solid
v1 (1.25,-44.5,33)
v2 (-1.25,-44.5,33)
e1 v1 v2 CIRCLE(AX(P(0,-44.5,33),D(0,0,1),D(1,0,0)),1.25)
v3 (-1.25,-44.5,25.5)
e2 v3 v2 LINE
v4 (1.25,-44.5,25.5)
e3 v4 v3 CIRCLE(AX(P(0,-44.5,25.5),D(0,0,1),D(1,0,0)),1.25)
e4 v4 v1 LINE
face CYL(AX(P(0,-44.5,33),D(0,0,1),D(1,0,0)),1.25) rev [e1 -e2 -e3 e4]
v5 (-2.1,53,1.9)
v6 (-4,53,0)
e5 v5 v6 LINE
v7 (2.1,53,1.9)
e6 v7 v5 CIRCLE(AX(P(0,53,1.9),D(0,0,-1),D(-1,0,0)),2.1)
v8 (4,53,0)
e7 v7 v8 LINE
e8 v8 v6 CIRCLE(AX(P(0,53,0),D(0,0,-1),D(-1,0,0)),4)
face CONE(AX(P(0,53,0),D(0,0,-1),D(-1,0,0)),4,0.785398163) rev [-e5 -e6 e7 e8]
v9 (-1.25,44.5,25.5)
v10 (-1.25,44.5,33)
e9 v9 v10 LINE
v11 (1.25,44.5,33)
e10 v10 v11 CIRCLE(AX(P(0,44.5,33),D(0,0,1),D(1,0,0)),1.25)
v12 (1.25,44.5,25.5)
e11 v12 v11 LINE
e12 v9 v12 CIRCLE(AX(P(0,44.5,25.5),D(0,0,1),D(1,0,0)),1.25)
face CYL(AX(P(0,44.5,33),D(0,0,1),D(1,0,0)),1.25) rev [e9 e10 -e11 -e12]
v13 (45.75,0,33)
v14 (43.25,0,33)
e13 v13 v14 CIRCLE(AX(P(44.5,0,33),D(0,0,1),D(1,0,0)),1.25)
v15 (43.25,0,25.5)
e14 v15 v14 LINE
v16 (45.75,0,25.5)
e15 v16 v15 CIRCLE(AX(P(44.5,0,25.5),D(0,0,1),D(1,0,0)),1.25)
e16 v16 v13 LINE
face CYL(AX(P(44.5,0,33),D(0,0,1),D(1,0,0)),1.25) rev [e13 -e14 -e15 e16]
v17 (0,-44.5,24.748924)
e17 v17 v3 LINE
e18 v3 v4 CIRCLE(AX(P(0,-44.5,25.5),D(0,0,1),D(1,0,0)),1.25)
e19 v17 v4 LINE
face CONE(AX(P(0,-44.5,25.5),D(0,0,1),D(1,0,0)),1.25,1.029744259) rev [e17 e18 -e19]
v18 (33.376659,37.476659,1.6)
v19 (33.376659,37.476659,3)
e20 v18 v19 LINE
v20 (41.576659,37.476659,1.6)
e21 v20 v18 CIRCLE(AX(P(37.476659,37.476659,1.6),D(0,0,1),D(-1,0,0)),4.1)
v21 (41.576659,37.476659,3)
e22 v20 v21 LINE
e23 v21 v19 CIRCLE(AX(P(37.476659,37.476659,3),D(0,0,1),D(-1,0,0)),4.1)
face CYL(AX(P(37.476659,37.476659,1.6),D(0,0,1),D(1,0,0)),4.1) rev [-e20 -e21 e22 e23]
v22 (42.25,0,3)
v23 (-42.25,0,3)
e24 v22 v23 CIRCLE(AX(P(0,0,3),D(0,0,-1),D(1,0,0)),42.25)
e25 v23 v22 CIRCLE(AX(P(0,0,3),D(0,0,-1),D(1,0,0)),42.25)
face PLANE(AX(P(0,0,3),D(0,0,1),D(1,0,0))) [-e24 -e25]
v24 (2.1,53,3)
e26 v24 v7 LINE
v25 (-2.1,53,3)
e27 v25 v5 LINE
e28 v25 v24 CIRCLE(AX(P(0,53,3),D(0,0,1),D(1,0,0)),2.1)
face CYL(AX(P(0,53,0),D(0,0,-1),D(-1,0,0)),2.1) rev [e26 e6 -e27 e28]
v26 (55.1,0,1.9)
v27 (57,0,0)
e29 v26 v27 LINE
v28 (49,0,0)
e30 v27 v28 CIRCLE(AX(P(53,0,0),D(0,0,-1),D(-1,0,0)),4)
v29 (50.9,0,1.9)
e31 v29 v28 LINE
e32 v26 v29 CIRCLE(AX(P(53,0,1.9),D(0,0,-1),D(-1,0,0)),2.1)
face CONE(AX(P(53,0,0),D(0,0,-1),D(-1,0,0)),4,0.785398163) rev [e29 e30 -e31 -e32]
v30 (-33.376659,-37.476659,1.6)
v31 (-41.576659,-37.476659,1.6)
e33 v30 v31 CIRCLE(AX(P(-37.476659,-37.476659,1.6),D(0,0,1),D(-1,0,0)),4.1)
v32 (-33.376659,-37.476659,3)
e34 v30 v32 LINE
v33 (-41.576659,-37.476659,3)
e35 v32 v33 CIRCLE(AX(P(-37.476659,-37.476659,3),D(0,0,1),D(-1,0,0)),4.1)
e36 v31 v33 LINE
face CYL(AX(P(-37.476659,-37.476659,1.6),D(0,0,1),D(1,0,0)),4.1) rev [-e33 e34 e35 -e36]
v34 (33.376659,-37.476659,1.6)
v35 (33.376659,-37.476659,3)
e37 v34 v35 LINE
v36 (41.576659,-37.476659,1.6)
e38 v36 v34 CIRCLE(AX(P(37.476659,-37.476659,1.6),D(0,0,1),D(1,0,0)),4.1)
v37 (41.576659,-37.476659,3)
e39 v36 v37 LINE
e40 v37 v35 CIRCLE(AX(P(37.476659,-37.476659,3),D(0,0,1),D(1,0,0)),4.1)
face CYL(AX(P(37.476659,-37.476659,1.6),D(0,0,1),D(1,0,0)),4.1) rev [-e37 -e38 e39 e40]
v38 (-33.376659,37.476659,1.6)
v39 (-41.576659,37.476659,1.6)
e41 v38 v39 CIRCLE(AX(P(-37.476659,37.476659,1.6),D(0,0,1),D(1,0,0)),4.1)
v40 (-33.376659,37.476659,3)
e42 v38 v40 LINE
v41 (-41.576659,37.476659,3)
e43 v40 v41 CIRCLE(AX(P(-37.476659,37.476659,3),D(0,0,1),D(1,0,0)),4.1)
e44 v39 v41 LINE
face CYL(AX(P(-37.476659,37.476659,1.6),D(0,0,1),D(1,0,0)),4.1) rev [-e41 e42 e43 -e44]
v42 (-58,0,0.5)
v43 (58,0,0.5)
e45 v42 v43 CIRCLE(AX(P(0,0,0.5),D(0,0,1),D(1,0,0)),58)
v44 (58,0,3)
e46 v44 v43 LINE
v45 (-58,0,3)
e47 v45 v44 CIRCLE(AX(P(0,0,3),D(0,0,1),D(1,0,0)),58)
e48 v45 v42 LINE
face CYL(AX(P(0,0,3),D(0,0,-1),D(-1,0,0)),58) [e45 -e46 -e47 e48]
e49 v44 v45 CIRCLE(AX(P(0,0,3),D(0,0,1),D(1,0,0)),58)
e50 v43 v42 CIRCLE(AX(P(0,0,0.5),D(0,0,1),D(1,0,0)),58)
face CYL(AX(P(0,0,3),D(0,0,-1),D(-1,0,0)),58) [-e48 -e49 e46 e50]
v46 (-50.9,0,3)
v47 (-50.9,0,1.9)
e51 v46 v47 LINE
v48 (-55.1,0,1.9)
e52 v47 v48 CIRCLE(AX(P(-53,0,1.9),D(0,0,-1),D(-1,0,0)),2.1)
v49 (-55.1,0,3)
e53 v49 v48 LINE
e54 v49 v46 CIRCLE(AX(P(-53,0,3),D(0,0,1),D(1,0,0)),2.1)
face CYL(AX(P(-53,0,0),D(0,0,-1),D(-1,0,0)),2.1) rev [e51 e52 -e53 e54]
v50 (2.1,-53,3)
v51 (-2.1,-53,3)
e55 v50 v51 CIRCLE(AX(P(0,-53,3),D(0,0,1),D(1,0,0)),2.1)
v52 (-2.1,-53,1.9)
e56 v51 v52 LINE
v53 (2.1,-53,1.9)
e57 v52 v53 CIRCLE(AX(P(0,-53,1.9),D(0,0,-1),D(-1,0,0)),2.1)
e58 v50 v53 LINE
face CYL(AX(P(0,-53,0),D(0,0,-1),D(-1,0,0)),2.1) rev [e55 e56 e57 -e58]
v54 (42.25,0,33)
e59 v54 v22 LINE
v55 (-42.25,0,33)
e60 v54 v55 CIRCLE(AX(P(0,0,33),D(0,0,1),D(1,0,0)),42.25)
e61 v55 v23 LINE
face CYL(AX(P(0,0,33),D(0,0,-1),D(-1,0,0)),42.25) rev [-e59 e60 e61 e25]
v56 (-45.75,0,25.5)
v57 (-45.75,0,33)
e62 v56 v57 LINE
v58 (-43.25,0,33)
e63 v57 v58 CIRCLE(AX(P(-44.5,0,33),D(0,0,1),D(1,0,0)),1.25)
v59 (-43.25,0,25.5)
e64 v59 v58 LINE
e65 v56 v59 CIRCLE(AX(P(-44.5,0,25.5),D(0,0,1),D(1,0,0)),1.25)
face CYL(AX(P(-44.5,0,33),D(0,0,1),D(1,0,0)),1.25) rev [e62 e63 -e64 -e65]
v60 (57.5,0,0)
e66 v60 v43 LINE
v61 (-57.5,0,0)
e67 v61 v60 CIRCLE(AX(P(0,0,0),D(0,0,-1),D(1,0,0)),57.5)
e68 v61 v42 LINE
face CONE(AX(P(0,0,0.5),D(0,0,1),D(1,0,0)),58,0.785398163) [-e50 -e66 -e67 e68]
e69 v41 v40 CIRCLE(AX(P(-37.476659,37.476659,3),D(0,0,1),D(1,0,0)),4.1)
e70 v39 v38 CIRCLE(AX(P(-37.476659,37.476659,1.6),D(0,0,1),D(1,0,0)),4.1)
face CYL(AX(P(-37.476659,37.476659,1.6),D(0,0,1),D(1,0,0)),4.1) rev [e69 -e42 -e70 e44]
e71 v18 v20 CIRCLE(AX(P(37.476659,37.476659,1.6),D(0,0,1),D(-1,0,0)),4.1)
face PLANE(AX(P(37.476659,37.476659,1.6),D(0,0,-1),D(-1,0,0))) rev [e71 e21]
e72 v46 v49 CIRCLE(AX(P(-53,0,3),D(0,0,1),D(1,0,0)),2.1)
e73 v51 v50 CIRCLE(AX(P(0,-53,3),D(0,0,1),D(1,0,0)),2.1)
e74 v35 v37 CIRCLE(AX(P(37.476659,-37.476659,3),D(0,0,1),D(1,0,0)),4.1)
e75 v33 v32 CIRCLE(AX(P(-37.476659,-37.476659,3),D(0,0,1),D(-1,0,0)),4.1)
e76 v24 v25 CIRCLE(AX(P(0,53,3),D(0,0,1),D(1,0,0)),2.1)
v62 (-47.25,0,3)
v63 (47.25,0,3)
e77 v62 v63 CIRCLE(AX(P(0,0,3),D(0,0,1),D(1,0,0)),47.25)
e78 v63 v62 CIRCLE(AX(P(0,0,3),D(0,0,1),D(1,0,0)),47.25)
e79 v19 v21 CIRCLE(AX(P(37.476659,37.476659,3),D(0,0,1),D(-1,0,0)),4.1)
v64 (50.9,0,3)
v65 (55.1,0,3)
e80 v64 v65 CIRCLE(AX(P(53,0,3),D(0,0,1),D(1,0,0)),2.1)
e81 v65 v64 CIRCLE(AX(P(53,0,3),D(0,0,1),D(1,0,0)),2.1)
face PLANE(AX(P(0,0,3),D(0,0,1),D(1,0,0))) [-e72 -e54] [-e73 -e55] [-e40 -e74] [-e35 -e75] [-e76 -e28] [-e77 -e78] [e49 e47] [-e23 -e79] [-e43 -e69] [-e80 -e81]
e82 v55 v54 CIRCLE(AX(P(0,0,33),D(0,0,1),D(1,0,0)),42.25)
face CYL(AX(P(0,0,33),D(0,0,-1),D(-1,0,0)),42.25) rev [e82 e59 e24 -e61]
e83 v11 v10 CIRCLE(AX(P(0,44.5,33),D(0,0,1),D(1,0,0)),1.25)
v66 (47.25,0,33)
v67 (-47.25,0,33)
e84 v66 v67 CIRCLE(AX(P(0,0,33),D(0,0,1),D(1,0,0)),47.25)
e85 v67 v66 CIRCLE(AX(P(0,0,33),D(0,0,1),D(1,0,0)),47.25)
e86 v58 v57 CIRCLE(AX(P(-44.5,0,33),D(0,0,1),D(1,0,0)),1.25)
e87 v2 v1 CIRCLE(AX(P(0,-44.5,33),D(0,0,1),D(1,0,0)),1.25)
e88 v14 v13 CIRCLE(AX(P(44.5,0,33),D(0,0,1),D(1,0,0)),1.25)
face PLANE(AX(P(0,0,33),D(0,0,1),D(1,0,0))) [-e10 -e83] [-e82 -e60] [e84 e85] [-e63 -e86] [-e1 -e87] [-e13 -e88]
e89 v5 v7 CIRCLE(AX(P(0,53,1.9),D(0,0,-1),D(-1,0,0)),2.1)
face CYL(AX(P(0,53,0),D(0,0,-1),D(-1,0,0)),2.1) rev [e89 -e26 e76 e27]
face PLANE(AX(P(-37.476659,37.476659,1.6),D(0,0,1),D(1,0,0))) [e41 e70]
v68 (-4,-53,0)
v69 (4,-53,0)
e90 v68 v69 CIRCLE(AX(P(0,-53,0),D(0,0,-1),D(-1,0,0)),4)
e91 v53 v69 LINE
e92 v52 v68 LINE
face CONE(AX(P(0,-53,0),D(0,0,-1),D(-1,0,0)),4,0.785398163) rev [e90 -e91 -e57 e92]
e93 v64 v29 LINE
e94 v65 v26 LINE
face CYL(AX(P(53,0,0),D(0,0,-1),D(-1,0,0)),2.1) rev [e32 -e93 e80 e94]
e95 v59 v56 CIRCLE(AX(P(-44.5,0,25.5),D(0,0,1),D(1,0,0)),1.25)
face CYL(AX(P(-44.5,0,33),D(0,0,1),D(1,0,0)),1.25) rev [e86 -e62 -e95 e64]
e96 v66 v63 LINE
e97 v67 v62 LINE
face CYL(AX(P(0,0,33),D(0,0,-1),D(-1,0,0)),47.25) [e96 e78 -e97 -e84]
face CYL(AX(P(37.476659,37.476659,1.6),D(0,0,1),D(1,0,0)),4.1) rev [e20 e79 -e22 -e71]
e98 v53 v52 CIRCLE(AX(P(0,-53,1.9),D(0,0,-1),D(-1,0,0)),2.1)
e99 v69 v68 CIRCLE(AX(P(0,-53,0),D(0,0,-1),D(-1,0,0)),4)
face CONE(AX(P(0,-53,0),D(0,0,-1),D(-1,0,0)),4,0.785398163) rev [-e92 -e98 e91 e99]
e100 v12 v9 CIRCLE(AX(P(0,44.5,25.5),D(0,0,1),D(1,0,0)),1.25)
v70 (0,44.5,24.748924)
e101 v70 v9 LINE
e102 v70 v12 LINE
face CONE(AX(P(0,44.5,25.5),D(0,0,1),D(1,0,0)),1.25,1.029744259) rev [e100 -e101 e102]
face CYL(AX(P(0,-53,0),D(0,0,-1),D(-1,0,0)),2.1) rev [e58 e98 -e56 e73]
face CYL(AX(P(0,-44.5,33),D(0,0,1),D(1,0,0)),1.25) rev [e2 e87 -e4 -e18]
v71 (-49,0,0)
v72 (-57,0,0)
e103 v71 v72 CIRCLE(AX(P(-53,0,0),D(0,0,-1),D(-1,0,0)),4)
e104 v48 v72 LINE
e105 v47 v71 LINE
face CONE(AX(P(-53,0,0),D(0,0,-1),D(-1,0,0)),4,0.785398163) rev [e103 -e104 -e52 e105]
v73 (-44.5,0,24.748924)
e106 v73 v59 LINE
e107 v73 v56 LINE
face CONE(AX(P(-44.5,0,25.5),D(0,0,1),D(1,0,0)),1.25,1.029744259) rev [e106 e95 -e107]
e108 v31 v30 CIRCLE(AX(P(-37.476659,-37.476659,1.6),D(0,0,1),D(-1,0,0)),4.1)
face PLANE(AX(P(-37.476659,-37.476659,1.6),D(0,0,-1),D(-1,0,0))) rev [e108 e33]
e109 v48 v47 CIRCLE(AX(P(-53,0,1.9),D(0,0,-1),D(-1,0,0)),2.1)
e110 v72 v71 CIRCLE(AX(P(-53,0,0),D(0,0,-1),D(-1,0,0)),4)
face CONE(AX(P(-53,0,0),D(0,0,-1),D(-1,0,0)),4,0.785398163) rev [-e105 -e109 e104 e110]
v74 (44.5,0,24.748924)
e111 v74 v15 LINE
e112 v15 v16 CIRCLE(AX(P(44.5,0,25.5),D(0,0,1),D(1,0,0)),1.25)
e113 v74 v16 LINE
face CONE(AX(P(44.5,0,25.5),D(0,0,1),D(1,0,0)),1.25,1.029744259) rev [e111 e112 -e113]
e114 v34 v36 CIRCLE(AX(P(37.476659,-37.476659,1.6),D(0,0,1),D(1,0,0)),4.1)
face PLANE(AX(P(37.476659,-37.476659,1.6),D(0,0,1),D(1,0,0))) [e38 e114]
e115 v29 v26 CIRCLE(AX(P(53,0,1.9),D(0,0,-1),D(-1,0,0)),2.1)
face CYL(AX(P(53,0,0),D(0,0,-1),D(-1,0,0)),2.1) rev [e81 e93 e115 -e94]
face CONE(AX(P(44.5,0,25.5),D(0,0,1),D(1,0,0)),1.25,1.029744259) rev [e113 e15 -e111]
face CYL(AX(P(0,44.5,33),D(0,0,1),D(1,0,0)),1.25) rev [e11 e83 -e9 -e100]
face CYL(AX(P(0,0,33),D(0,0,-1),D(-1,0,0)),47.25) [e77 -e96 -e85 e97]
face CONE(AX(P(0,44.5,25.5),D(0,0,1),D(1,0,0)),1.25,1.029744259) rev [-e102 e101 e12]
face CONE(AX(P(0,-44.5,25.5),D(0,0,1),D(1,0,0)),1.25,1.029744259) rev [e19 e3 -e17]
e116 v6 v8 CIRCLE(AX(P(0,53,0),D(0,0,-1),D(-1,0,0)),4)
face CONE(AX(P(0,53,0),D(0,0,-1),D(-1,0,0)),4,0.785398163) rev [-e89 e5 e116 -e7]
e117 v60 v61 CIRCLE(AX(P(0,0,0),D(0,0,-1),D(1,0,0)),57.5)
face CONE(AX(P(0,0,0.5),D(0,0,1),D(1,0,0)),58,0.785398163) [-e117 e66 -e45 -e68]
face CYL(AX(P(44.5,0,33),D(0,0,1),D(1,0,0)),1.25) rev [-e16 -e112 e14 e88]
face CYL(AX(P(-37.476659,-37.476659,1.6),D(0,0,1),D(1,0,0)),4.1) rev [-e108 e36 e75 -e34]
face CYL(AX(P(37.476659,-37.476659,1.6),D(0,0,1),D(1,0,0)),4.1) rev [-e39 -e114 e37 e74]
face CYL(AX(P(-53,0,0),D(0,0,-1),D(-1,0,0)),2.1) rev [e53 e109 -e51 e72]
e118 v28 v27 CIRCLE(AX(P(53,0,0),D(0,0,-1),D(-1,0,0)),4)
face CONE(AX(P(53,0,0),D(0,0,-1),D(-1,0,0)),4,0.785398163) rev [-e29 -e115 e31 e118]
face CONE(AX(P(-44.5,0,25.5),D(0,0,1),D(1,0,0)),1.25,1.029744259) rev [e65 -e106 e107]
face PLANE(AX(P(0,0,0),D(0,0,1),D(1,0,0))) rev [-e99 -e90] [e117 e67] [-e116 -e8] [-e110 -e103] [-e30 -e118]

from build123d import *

# Parameters (mm, degrees)
SKETCH_1_R                   = 58
EXTRUDE_1_DEPTH              = 3
SKETCH_2_R                   = 47.25
SKETCH_2_R_2                 = 42.25
EXTRUDE_2_DEPTH              = 30
CHAMFER_1_SIZE               = 0.5
HOLE_WIZARD_M4_1_D           = 4.2
HOLE_WIZARD_M4_1_DEPTH       = 10.1
HOLE_WIZARD_M4_1_CSINK_D     = 8
HOLE_WIZARD_M4_1_CSINK_ANGLE = 90
HOLE_WIZARD_M4_1_TIP         = 1.2618073
HOLE_WIZARD_M3_2_D           = 2.5
HOLE_WIZARD_M3_2_DEPTH       = 7.5
HOLE_WIZARD_M3_2_TIP         = 0.751075774
SKETCH_32_R                  = 4.1
CUT_EXTRUDE_12_DEPTH         = 1.4


with BuildPart() as part:
    # 草图1 → 凸台-拉伸1 (new body)
    with BuildSketch(Plane.XY):
        Circle(SKETCH_1_R)
    extrude(amount=EXTRUDE_1_DEPTH)

    # 草图2 → 凸台-拉伸2 (add)
    with BuildSketch(Plane.XY.offset(3)):
        Circle(SKETCH_2_R)
        Circle(SKETCH_2_R_2, mode=Mode.SUBTRACT)
    extrude(amount=EXTRUDE_2_DEPTH)

    # 倒角1
    chamfer_1_edges = [part.edges().sort_by_distance(p)[0] for p in [
        (-58, 0, 0),
    ]]
    chamfer(chamfer_1_edges, length=CHAMFER_1_SIZE)

    # M4 六角凹锥坑螺钉的锥形沉头孔1
    with Locations(Plane(origin=(0, 0, 0), x_dir=(-1, 0, 0), z_dir=(0, 0, -1))):
        with Locations((0, 53), (53, 0), (0, -53), (-53, 0)):
            CounterSinkHole(HOLE_WIZARD_M4_1_D / 2, HOLE_WIZARD_M4_1_CSINK_D / 2, depth=HOLE_WIZARD_M4_1_DEPTH, counter_sink_angle=HOLE_WIZARD_M4_1_CSINK_ANGLE)
            with Locations((0, 0, -(HOLE_WIZARD_M4_1_DEPTH + HOLE_WIZARD_M4_1_TIP / 2))):  # 118° drill point
                Cone(0, HOLE_WIZARD_M4_1_D / 2, HOLE_WIZARD_M4_1_TIP, mode=Mode.SUBTRACT)

    # M3 螺纹孔2
    with Locations(Plane.XY.offset(33)):
        with Locations((0, 44.5), (44.5, 0), (0, -44.5), (-44.5, 0), (0, 0)):
            Hole(HOLE_WIZARD_M3_2_D / 2, depth=HOLE_WIZARD_M3_2_DEPTH)
            with Locations((0, 0, -(HOLE_WIZARD_M3_2_DEPTH + HOLE_WIZARD_M3_2_TIP / 2))):  # 118° drill point
                Cone(0, HOLE_WIZARD_M3_2_D / 2, HOLE_WIZARD_M3_2_TIP, mode=Mode.SUBTRACT)

    # 草图32 → 切除-拉伸12 (cut)
    with BuildSketch(Plane.XY.offset(3)):
        with Locations((37.476659403, -37.476659403)):
            Circle(SKETCH_32_R)
        with Locations(Location((37.476659403, 37.476659403, 0), (0, 0, 180))):
            Circle(SKETCH_32_R)
        with Locations((-37.476659403, 37.476659403)):
            Circle(SKETCH_32_R)
        with Locations(Location((-37.476659403, -37.476659403, 0), (0, 0, 180))):
            Circle(SKETCH_32_R)
    extrude(amount=-CUT_EXTRUDE_12_DEPTH, mode=Mode.SUBTRACT)


solid = part.part
